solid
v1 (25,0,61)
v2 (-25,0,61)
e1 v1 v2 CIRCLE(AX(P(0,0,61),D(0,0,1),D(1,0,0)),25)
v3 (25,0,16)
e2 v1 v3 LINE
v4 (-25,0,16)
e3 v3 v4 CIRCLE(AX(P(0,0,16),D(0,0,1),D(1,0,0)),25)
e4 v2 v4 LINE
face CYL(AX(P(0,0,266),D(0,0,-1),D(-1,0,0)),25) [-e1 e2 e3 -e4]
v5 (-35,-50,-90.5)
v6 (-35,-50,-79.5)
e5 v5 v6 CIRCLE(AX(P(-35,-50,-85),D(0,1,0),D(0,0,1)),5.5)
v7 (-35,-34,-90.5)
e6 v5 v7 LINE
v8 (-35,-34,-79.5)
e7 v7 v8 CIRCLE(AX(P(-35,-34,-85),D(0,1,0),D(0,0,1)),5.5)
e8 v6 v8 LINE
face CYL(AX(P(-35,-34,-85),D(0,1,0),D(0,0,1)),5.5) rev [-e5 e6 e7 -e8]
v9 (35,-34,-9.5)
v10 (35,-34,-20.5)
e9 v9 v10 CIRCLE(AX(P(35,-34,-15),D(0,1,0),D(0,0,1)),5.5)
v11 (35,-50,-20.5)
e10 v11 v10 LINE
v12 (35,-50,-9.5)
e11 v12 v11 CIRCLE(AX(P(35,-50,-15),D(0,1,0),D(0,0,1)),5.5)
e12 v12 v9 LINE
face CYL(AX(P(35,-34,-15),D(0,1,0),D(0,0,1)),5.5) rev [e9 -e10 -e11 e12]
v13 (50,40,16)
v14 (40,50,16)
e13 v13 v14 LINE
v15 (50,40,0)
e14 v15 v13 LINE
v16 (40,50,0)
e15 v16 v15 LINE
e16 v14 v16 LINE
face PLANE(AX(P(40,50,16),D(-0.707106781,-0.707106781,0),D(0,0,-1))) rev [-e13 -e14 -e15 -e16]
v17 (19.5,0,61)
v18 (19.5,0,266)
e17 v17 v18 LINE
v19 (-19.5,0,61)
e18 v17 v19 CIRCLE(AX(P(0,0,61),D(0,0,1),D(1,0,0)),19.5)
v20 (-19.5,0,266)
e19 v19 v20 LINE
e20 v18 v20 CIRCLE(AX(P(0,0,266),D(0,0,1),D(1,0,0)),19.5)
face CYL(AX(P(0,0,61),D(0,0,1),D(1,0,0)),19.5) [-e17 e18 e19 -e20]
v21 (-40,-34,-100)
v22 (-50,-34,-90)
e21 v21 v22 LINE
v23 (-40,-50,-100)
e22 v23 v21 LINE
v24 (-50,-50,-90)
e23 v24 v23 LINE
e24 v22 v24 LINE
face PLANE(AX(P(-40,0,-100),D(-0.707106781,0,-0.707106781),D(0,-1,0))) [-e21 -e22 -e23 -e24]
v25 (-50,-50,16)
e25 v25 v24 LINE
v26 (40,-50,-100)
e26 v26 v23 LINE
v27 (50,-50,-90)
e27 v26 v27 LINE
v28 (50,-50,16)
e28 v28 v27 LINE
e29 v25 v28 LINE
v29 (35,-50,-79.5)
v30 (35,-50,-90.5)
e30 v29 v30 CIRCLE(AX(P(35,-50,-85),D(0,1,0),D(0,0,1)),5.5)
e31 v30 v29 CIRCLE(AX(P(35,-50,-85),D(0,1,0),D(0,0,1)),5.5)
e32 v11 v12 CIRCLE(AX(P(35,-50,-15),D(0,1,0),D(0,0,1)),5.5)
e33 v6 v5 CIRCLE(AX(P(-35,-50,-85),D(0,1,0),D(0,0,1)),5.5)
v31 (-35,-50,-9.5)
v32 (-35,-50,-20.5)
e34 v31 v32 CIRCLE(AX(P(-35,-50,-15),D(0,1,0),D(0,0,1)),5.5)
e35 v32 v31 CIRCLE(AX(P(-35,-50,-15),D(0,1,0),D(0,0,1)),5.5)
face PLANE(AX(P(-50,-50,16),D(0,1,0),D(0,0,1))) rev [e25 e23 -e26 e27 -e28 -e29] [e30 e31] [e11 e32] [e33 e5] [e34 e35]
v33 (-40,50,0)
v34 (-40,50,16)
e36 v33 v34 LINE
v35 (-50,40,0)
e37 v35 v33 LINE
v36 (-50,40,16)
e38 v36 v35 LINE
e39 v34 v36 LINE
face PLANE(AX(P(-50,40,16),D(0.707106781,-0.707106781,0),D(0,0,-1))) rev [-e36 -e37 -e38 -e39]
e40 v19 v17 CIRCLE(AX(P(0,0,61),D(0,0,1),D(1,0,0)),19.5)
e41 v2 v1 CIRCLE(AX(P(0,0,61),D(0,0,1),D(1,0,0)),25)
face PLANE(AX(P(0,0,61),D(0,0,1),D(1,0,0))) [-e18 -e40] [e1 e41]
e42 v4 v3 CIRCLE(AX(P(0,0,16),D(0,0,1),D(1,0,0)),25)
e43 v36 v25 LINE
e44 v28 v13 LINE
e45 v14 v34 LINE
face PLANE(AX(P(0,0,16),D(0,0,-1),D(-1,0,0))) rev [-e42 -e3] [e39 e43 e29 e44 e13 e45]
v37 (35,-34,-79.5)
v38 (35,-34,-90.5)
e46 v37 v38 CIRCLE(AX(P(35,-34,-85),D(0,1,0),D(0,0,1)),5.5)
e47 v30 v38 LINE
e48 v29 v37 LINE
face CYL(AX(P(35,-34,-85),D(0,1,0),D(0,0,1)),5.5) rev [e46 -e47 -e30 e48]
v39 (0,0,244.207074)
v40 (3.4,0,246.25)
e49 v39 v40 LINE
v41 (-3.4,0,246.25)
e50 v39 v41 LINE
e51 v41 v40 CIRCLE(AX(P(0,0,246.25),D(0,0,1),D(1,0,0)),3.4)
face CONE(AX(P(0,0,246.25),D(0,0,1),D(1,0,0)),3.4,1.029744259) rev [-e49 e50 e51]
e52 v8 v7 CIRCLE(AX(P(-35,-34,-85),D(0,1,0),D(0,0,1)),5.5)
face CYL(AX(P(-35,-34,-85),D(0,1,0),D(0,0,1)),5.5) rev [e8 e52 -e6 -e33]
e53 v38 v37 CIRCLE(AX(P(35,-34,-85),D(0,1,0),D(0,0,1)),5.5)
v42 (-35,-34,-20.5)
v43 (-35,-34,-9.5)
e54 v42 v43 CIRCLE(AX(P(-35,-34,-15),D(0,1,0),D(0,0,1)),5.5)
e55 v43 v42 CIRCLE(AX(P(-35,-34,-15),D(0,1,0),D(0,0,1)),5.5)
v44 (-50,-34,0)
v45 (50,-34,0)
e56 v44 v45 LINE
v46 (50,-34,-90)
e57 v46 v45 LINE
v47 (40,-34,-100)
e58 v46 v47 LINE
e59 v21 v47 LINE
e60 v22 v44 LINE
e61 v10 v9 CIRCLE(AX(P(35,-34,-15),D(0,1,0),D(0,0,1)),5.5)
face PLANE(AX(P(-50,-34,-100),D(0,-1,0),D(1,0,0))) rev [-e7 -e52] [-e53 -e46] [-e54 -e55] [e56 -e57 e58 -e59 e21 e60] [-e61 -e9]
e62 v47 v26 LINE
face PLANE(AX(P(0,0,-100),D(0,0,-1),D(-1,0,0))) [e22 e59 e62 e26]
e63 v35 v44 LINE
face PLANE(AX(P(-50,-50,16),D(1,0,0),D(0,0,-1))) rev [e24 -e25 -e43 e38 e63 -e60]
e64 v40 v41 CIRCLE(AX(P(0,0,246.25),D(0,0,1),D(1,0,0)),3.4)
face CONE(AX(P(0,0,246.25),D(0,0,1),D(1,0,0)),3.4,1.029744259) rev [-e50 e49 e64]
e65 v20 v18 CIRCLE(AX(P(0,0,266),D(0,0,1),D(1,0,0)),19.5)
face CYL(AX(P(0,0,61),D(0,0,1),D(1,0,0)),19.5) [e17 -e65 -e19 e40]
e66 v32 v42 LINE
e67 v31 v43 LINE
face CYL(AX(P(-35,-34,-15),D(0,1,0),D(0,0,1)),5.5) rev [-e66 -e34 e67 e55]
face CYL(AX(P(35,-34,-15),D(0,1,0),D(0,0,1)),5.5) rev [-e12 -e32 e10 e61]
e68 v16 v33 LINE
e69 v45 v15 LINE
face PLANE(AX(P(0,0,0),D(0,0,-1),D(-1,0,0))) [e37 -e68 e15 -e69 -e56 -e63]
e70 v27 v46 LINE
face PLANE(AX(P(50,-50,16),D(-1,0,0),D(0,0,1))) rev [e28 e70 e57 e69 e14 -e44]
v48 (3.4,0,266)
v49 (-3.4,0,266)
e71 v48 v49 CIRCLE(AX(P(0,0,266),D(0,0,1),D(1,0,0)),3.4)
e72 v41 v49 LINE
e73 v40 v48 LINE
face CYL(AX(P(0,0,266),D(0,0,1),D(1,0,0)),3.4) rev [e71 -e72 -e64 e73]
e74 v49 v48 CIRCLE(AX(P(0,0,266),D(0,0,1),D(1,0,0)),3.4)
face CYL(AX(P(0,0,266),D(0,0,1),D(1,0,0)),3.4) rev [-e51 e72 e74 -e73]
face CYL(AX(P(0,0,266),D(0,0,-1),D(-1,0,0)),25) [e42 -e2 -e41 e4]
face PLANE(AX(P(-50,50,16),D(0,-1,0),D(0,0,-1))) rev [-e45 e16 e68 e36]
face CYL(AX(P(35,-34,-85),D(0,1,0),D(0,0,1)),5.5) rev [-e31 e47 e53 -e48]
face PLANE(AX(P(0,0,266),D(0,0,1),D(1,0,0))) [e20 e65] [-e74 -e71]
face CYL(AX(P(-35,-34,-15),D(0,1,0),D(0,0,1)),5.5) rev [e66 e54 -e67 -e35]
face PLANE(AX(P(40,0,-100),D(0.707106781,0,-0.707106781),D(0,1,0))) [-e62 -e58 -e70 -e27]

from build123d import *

# Parameters (mm, degrees)
SKETCH_1_W             = 100
SKETCH_1_H             = 100
EXTRUDE_1_DEPTH        = 16
SKETCH_2_R             = 25
EXTRUDE_2_DEPTH        = 250
SKETCH_3_OUTSIDE_W     = 162.252
SKETCH_3_OUTSIDE_H     = 162.252
SKETCH_3_OUTSIDE_R     = 19.5
CUT_EXTRUDE_1_DEPTH    = 205
SKETCH_8_W             = 100
SKETCH_8_H             = 16
EXTRUDE_3_DEPTH        = 100
HOLE_WIZARD_M8_1_D     = 6.8
HOLE_WIZARD_M8_1_DEPTH = 19.75
HOLE_WIZARD_M8_1_TIP   = 2.042926105
HOLE_WIZARD_M10_1_D    = 11
CHAMFER_1_SIZE         = 10


with BuildPart() as part:
    # 草图1 → 凸台-拉伸1 (new body)
    with BuildSketch(Plane.XY):
        Rectangle(SKETCH_1_W, SKETCH_1_H)
    extrude(amount=EXTRUDE_1_DEPTH)

    # 草图2 → 凸台-拉伸2 (add)
    with BuildSketch(Plane.XY.offset(16)):
        Circle(SKETCH_2_R)
    extrude(amount=EXTRUDE_2_DEPTH)

    # 草图3 outside → 切除-拉伸1 (cut)
    with BuildSketch(Plane.XY.offset(266)):
        Rectangle(SKETCH_3_OUTSIDE_W, SKETCH_3_OUTSIDE_H)
        Circle(SKETCH_3_OUTSIDE_R, mode=Mode.SUBTRACT)
    extrude(amount=-CUT_EXTRUDE_1_DEPTH, mode=Mode.SUBTRACT)

    # 草图8 → 凸台-拉伸3 (add)
    with BuildSketch(Plane(origin=(0, 0, 0), x_dir=(-1, 0, 0), z_dir=(0, 0, -1))):
        with Locations((0, -42)):
            Rectangle(SKETCH_8_W, SKETCH_8_H)
    extrude(amount=EXTRUDE_3_DEPTH)

    # M8 螺纹孔1
    with Locations(Plane.XY.offset(266)):
        with Locations((0, 0)):
            Hole(HOLE_WIZARD_M8_1_D / 2, depth=HOLE_WIZARD_M8_1_DEPTH)
            with Locations((0, 0, -(HOLE_WIZARD_M8_1_DEPTH + HOLE_WIZARD_M8_1_TIP / 2))):  # 118° drill point
                Cone(0, HOLE_WIZARD_M8_1_D / 2, HOLE_WIZARD_M8_1_TIP, mode=Mode.SUBTRACT)

    # M10 间隙孔1 (through all)
    with Locations(Plane(origin=(0, -34, -18), x_dir=(1, 0, 0), z_dir=(0, 1, 0))):
        with Locations((-35, 67), (35, 67), (35, -3), (-35, -3)):
            Hole(HOLE_WIZARD_M10_1_D / 2)

    # 倒角1
    chamfer_1_edges = [part.edges().sort_by_distance(p)[0] for p in [
        (-50, -42, -100),
        (50, -42, -100),
        (-50, 50, 8),
        (50, 50, 8),
    ]]
    chamfer(chamfer_1_edges, length=CHAMFER_1_SIZE)


solid = part.part
